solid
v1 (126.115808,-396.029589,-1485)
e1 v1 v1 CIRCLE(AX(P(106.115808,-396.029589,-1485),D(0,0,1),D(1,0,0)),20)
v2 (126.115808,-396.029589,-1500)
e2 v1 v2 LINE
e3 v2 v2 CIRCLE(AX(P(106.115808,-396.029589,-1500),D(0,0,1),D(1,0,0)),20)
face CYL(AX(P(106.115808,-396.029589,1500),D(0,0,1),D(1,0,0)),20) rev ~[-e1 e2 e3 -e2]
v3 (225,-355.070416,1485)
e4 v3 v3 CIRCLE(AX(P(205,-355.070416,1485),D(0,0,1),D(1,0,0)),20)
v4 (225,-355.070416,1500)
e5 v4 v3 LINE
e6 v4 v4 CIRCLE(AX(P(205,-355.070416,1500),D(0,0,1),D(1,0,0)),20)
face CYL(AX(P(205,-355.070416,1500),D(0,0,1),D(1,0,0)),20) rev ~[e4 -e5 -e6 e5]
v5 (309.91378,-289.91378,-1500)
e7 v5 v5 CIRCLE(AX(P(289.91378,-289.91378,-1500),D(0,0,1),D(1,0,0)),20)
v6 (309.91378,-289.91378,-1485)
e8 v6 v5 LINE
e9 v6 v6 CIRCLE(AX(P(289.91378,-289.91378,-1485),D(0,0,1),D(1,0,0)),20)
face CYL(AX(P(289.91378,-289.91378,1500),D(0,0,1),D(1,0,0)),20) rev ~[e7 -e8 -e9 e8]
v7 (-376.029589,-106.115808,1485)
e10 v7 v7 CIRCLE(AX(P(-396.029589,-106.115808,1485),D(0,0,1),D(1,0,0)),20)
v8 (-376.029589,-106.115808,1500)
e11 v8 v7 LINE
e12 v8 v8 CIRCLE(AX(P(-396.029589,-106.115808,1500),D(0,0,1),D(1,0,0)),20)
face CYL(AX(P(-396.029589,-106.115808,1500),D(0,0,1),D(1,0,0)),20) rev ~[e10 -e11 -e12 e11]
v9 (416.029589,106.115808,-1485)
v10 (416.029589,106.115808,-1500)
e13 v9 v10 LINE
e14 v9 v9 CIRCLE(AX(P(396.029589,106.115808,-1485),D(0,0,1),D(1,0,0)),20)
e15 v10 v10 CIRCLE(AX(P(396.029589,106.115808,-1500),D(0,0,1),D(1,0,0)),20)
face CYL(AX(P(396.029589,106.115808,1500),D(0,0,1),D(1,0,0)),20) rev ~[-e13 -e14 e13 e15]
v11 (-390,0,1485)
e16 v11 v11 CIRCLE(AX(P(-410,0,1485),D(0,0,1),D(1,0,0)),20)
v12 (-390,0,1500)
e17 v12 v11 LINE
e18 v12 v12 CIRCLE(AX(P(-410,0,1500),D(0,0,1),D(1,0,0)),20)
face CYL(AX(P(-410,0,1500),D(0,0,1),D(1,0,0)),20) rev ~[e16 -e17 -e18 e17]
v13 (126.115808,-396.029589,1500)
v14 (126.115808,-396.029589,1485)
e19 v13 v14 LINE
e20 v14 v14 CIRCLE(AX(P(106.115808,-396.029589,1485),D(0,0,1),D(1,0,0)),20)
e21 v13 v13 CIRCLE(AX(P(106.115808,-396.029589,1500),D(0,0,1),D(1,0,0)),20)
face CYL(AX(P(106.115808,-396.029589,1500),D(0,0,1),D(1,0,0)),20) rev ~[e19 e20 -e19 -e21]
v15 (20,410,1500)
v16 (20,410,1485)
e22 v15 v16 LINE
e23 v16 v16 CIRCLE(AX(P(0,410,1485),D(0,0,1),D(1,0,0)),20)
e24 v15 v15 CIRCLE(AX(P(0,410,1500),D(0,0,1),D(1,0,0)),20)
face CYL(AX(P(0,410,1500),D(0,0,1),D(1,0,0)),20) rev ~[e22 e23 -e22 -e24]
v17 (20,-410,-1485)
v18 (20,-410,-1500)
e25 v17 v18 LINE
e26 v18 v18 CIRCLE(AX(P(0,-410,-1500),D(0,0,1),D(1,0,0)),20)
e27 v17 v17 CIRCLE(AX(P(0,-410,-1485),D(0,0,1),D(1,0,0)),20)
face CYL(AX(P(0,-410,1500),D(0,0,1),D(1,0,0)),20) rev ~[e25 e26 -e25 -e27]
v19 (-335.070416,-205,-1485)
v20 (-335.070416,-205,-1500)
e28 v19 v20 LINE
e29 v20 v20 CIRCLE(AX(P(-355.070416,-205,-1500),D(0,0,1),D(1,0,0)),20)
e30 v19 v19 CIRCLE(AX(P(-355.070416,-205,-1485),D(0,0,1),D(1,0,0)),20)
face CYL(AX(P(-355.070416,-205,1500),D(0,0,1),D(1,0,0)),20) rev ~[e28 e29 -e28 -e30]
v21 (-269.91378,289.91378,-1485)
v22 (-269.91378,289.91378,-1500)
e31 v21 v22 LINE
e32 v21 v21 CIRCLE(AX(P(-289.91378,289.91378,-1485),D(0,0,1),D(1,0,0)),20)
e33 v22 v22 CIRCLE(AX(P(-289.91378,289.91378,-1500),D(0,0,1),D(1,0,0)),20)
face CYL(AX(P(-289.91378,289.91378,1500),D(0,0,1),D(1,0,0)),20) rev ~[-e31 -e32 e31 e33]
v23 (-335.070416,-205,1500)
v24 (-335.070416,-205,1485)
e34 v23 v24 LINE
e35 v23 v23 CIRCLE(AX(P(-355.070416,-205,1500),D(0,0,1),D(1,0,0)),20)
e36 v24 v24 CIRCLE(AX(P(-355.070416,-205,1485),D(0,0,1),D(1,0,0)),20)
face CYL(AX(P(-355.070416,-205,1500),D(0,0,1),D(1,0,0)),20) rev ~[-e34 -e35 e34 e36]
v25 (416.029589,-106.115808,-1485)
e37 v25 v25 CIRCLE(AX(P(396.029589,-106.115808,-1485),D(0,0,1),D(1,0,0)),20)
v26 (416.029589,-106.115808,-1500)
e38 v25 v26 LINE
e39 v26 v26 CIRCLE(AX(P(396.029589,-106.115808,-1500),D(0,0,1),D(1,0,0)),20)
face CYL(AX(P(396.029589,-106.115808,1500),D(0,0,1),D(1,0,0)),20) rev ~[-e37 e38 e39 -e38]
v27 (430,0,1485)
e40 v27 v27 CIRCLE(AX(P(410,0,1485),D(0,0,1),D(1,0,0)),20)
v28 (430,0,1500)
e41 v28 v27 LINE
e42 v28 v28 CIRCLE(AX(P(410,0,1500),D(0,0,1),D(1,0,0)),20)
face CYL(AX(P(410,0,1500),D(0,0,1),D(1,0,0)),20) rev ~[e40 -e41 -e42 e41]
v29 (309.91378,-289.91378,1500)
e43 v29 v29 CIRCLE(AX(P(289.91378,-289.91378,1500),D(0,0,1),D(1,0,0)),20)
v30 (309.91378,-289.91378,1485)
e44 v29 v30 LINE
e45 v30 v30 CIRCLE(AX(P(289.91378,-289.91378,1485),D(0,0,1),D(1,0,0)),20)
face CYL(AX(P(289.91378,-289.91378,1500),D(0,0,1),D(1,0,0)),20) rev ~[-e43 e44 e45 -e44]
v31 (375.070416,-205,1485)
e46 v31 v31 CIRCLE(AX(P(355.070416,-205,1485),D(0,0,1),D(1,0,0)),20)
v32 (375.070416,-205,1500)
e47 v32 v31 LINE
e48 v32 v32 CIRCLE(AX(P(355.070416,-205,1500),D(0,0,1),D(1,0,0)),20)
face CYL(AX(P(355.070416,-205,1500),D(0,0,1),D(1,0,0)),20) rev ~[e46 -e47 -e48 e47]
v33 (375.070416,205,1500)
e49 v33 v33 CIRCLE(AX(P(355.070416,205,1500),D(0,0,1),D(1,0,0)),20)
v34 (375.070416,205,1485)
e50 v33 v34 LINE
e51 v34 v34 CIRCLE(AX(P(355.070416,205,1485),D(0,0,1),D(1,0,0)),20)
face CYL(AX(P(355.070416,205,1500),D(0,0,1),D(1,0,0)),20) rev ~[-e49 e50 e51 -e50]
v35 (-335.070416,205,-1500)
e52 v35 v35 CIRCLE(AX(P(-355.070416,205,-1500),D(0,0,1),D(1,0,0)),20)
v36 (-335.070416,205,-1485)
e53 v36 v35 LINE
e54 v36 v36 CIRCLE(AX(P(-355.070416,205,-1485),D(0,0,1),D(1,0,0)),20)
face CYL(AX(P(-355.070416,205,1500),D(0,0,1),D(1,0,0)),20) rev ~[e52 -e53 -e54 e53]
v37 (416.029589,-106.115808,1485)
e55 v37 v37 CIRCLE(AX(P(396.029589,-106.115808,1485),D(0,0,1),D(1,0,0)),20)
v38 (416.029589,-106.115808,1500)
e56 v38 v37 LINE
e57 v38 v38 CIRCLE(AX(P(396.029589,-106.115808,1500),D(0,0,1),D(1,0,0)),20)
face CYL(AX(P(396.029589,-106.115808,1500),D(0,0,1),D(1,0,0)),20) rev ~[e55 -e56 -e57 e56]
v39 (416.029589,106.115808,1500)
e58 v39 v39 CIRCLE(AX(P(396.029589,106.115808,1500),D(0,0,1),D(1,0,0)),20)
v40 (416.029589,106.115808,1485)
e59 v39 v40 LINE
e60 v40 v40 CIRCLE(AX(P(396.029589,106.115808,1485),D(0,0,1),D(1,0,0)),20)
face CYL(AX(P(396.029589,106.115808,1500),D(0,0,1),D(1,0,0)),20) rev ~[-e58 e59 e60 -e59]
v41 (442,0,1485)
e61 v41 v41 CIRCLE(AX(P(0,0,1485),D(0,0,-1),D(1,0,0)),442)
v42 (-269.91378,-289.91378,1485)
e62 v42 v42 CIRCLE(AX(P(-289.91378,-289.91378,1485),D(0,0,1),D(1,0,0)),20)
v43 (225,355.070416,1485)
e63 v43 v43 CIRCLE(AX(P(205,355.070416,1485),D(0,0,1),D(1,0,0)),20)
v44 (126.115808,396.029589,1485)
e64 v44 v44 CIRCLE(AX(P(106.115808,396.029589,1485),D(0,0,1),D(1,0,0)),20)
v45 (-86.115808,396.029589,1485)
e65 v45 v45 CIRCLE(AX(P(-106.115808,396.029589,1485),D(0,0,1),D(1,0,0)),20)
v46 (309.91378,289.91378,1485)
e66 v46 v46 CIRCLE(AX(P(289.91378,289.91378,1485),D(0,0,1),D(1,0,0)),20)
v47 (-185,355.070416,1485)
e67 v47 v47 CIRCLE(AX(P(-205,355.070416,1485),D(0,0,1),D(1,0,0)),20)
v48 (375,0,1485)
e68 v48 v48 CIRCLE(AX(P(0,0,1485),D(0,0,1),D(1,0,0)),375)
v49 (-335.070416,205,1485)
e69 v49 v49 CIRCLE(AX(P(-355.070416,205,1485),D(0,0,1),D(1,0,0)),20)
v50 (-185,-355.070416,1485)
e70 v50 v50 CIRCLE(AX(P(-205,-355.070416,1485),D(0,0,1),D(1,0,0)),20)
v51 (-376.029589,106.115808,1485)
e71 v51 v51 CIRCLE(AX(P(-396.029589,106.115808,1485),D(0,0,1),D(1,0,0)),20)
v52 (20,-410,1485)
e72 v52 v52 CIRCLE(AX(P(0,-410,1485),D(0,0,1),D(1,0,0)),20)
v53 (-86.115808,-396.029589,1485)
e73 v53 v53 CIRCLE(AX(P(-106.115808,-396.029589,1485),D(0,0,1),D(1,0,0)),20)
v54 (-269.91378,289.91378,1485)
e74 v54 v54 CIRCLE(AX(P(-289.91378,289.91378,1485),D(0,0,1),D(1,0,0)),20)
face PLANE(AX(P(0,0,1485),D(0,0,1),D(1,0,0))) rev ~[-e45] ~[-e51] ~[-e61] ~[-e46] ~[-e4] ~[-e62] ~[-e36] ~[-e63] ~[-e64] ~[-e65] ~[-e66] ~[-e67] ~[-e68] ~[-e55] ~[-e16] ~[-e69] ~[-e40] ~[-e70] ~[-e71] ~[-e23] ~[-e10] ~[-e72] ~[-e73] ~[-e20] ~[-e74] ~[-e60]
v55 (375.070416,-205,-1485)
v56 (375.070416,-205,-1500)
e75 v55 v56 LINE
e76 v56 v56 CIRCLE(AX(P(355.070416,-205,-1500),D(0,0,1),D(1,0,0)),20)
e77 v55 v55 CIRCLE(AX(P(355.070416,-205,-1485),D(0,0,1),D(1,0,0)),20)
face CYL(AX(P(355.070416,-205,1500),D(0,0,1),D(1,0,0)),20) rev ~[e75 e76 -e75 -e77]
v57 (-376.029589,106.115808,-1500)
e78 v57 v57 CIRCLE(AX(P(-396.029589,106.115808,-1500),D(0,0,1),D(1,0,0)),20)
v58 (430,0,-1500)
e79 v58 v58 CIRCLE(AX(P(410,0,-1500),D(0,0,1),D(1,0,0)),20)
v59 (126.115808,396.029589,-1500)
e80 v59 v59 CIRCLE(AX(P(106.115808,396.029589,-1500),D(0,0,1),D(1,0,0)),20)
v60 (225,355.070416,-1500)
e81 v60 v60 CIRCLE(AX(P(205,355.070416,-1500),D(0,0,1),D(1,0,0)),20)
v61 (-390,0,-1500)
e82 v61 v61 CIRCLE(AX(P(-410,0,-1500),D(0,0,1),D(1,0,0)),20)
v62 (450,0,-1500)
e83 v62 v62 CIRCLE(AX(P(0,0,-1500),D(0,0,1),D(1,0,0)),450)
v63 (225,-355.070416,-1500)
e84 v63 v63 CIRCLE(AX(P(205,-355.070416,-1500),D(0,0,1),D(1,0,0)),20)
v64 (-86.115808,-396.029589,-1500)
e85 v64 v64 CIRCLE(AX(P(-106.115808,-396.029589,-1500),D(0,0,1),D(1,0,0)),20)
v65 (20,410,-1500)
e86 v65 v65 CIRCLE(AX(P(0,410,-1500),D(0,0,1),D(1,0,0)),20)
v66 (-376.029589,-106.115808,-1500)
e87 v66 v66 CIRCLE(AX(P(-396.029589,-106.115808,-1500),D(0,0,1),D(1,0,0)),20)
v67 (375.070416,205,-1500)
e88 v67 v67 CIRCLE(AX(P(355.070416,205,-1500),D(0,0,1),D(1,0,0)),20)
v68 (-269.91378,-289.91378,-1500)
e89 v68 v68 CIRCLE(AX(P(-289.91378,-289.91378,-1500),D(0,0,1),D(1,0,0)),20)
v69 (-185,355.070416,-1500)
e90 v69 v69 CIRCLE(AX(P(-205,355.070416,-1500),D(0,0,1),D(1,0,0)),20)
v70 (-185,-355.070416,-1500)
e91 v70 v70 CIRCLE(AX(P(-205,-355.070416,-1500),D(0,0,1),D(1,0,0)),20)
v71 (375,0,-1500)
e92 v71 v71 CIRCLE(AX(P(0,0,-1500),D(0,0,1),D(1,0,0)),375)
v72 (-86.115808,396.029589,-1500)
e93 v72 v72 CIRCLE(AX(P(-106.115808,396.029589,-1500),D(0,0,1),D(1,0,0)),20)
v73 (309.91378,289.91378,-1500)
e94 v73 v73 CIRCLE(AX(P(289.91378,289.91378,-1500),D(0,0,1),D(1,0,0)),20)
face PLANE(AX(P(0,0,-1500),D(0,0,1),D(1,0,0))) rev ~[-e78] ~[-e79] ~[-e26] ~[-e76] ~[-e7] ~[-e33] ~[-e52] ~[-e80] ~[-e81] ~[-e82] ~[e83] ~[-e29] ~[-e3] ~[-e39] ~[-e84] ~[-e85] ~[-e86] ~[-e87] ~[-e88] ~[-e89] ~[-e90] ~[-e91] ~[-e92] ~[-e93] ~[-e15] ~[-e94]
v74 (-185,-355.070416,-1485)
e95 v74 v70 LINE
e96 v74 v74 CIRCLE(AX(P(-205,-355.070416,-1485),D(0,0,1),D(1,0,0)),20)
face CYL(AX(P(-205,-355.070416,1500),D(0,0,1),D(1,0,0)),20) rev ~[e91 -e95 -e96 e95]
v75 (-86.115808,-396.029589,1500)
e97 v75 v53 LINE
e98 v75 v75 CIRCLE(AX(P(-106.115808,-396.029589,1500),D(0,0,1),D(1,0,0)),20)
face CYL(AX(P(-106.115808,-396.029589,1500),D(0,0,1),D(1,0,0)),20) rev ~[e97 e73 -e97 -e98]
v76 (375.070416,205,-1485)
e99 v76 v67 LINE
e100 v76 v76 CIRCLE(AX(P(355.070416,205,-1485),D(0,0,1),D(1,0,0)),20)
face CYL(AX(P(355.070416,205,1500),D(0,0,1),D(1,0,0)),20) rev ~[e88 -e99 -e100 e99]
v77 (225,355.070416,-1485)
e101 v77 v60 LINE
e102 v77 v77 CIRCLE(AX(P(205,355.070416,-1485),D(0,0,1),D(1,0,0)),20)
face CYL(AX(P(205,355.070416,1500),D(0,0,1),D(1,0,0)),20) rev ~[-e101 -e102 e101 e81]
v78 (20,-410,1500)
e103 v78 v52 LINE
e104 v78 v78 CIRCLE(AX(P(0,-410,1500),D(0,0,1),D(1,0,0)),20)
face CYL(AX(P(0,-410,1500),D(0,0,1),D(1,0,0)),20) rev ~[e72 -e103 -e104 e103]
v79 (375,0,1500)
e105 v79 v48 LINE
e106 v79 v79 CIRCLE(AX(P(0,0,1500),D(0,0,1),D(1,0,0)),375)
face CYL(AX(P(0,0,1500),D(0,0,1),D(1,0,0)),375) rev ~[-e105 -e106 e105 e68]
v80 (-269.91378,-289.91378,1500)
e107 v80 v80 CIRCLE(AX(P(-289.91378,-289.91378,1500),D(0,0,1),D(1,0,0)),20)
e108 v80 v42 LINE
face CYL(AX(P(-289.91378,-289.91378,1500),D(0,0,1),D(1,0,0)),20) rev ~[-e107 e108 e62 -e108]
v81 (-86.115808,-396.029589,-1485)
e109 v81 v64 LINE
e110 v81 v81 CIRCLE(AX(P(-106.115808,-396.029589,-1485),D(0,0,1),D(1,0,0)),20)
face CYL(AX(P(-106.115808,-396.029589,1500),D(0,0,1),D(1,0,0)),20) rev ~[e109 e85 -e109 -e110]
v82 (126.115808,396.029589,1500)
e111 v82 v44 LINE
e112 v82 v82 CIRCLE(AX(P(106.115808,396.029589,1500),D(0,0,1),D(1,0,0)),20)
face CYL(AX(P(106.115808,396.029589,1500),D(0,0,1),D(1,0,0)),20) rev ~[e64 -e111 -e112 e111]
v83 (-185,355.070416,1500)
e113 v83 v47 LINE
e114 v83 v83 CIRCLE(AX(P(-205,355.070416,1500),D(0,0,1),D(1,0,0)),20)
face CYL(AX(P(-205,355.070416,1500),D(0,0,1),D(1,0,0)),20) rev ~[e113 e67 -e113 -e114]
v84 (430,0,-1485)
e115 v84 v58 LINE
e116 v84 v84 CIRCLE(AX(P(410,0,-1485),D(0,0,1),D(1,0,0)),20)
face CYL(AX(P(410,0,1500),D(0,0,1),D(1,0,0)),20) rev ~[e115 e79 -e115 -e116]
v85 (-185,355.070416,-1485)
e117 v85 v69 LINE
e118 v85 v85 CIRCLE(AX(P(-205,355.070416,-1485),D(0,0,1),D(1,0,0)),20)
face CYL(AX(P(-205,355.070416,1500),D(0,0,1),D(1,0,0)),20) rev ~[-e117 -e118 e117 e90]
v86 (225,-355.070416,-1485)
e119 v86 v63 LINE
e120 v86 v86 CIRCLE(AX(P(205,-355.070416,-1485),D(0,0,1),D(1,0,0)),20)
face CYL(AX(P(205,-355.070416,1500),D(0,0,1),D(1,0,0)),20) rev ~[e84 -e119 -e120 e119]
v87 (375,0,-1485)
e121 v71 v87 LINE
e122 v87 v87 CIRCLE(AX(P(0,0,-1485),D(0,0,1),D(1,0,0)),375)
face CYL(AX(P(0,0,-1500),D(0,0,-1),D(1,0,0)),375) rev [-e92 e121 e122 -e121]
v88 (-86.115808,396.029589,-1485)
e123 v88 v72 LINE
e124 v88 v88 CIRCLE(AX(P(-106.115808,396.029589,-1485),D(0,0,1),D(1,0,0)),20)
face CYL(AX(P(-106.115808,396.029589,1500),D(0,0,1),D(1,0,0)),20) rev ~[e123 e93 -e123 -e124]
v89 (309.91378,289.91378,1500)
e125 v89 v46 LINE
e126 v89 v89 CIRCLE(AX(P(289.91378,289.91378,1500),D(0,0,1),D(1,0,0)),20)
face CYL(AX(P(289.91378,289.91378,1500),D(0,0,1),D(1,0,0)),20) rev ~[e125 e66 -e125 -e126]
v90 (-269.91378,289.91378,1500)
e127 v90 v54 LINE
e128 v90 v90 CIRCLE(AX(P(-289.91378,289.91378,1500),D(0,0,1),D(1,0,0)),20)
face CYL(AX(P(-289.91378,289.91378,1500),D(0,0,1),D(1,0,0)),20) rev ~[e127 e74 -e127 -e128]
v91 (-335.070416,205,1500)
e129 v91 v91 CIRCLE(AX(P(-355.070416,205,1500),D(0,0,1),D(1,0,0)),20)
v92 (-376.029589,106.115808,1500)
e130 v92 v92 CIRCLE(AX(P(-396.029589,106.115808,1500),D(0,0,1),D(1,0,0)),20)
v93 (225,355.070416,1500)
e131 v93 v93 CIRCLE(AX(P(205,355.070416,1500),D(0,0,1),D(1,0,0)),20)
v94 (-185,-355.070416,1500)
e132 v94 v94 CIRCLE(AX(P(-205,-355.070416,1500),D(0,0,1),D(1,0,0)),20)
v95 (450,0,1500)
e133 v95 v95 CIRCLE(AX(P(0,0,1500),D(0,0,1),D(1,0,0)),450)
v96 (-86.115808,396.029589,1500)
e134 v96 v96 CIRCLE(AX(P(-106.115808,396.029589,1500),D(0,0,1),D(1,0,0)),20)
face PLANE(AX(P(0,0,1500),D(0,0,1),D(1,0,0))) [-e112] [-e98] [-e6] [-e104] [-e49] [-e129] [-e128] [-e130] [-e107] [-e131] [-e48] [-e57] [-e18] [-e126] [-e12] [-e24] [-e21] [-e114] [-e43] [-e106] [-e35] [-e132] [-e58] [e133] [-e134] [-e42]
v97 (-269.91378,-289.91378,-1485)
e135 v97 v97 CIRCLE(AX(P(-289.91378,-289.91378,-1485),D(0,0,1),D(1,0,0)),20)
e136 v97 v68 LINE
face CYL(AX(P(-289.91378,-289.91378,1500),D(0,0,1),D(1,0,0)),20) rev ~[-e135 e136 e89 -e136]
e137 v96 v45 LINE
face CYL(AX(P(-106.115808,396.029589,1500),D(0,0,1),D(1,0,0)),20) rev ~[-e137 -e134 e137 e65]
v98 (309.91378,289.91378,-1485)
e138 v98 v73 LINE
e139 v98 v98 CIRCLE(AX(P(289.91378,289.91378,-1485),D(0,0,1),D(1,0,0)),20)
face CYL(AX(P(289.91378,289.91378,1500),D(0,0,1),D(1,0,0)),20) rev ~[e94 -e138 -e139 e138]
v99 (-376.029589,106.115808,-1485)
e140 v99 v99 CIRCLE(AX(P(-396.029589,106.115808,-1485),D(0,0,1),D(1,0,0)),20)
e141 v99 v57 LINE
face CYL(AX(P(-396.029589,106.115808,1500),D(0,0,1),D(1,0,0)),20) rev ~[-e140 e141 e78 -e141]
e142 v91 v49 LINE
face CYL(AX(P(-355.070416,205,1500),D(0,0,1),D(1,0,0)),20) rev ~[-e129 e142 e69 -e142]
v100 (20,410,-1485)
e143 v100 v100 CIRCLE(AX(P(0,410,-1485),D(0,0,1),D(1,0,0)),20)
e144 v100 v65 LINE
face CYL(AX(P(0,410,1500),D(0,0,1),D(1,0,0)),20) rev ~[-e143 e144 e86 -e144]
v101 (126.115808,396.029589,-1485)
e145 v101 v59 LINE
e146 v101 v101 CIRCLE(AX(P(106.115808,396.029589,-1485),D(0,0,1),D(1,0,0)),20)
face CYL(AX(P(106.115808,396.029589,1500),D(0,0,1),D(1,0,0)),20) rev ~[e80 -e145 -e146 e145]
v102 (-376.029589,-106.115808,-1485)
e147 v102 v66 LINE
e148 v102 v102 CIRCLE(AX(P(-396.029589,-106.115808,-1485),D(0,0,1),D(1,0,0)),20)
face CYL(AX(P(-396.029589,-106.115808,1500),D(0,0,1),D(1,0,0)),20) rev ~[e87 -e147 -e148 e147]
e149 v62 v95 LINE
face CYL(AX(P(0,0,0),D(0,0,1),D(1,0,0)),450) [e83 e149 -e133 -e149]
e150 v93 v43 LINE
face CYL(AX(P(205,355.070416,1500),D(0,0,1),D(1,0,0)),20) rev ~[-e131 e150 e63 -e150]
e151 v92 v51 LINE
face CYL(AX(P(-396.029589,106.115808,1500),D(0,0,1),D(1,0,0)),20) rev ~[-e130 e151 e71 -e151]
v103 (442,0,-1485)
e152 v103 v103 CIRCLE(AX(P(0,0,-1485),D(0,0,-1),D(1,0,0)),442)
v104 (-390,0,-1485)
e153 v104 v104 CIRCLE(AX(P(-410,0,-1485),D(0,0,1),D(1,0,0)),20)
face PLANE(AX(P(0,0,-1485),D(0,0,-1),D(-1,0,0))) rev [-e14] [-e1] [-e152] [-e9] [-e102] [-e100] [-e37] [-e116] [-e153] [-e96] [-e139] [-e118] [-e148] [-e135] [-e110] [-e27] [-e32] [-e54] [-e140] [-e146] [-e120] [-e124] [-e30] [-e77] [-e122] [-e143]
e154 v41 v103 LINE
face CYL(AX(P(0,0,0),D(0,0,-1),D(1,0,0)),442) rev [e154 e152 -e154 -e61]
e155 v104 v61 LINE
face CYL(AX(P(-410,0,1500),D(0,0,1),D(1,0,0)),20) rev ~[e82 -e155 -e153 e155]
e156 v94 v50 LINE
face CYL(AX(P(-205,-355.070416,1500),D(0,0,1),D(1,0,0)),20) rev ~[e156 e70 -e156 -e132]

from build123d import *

# Parameters (mm, degrees)
SKETCH_1_R          = 450
SKETCH_1_R_2        = 442
EXTRUDE_1_DEPTH     = 1500
SKETCH_2_R          = 450
SKETCH_2_R_2        = 375
EXTRUDE_3_DEPTH     = 15
SKETCH_3_R          = 20
CUT_EXTRUDE_1_DEPTH = 3067.757245039


with BuildPart() as part:
    # 草图1 → 凸台-拉伸1 (new, symmetric)
    with BuildSketch(Plane.XY):
        Circle(SKETCH_1_R)
        Circle(SKETCH_1_R_2, mode=Mode.SUBTRACT)
    extrude(amount=EXTRUDE_1_DEPTH, both=True)

    # 草图2 → 凸台-拉伸3 (add)
    with BuildSketch(Plane.XY.offset(1500)):
        Circle(SKETCH_2_R)
        Circle(SKETCH_2_R_2, mode=Mode.SUBTRACT)
    extrude_3 = extrude(amount=-EXTRUDE_3_DEPTH)

    # 镜向1: 凸台-拉伸3 across plane
    add(extrude_3.mirror(Plane.XY))

    # 草图3 → 切除-拉伸1 (cut, through all)
    with BuildSketch(Plane.XY.offset(1500)):
        with Locations((0, 410)):
            Circle(SKETCH_3_R)
        with Locations((106.115808492, 396.029588779)):
            Circle(SKETCH_3_R)
        with Locations((205, 355.070415552)):
            Circle(SKETCH_3_R)
        with Locations((289.913780286, 289.913780286)):
            Circle(SKETCH_3_R)
        with Locations((355.070415552, 205)):
            Circle(SKETCH_3_R)
        with Locations((396.029588779, 106.115808492)):
            Circle(SKETCH_3_R)
        with Locations((410, 0)):
            Circle(SKETCH_3_R)
        with Locations((396.029588779, -106.115808492)):
            Circle(SKETCH_3_R)
        with Locations((355.070415552, -205)):
            Circle(SKETCH_3_R)
        with Locations((289.913780286, -289.913780286)):
            Circle(SKETCH_3_R)
        with Locations((205, -355.070415552)):
            Circle(SKETCH_3_R)
        with Locations((106.115808492, -396.029588779)):
            Circle(SKETCH_3_R)
        with Locations((0, -410)):
            Circle(SKETCH_3_R)
        with Locations((-106.115808492, -396.029588779)):
            Circle(SKETCH_3_R)
        with Locations((-205, -355.070415552)):
            Circle(SKETCH_3_R)
        with Locations((-289.913780286, -289.913780286)):
            Circle(SKETCH_3_R)
        with Locations((-355.070415552, -205)):
            Circle(SKETCH_3_R)
        with Locations((-396.029588779, -106.115808492)):
            Circle(SKETCH_3_R)
        with Locations((-410, 0)):
            Circle(SKETCH_3_R)
        with Locations((-396.029588779, 106.115808492)):
            Circle(SKETCH_3_R)
        with Locations((-355.070415552, 205)):
            Circle(SKETCH_3_R)
        with Locations((-289.913780286, 289.913780286)):
            Circle(SKETCH_3_R)
        with Locations((-205, 355.070415552)):
            Circle(SKETCH_3_R)
        with Locations((-106.115808492, 396.029588779)):
            Circle(SKETCH_3_R)
    extrude(amount=-CUT_EXTRUDE_1_DEPTH, mode=Mode.SUBTRACT)


solid = part.part
